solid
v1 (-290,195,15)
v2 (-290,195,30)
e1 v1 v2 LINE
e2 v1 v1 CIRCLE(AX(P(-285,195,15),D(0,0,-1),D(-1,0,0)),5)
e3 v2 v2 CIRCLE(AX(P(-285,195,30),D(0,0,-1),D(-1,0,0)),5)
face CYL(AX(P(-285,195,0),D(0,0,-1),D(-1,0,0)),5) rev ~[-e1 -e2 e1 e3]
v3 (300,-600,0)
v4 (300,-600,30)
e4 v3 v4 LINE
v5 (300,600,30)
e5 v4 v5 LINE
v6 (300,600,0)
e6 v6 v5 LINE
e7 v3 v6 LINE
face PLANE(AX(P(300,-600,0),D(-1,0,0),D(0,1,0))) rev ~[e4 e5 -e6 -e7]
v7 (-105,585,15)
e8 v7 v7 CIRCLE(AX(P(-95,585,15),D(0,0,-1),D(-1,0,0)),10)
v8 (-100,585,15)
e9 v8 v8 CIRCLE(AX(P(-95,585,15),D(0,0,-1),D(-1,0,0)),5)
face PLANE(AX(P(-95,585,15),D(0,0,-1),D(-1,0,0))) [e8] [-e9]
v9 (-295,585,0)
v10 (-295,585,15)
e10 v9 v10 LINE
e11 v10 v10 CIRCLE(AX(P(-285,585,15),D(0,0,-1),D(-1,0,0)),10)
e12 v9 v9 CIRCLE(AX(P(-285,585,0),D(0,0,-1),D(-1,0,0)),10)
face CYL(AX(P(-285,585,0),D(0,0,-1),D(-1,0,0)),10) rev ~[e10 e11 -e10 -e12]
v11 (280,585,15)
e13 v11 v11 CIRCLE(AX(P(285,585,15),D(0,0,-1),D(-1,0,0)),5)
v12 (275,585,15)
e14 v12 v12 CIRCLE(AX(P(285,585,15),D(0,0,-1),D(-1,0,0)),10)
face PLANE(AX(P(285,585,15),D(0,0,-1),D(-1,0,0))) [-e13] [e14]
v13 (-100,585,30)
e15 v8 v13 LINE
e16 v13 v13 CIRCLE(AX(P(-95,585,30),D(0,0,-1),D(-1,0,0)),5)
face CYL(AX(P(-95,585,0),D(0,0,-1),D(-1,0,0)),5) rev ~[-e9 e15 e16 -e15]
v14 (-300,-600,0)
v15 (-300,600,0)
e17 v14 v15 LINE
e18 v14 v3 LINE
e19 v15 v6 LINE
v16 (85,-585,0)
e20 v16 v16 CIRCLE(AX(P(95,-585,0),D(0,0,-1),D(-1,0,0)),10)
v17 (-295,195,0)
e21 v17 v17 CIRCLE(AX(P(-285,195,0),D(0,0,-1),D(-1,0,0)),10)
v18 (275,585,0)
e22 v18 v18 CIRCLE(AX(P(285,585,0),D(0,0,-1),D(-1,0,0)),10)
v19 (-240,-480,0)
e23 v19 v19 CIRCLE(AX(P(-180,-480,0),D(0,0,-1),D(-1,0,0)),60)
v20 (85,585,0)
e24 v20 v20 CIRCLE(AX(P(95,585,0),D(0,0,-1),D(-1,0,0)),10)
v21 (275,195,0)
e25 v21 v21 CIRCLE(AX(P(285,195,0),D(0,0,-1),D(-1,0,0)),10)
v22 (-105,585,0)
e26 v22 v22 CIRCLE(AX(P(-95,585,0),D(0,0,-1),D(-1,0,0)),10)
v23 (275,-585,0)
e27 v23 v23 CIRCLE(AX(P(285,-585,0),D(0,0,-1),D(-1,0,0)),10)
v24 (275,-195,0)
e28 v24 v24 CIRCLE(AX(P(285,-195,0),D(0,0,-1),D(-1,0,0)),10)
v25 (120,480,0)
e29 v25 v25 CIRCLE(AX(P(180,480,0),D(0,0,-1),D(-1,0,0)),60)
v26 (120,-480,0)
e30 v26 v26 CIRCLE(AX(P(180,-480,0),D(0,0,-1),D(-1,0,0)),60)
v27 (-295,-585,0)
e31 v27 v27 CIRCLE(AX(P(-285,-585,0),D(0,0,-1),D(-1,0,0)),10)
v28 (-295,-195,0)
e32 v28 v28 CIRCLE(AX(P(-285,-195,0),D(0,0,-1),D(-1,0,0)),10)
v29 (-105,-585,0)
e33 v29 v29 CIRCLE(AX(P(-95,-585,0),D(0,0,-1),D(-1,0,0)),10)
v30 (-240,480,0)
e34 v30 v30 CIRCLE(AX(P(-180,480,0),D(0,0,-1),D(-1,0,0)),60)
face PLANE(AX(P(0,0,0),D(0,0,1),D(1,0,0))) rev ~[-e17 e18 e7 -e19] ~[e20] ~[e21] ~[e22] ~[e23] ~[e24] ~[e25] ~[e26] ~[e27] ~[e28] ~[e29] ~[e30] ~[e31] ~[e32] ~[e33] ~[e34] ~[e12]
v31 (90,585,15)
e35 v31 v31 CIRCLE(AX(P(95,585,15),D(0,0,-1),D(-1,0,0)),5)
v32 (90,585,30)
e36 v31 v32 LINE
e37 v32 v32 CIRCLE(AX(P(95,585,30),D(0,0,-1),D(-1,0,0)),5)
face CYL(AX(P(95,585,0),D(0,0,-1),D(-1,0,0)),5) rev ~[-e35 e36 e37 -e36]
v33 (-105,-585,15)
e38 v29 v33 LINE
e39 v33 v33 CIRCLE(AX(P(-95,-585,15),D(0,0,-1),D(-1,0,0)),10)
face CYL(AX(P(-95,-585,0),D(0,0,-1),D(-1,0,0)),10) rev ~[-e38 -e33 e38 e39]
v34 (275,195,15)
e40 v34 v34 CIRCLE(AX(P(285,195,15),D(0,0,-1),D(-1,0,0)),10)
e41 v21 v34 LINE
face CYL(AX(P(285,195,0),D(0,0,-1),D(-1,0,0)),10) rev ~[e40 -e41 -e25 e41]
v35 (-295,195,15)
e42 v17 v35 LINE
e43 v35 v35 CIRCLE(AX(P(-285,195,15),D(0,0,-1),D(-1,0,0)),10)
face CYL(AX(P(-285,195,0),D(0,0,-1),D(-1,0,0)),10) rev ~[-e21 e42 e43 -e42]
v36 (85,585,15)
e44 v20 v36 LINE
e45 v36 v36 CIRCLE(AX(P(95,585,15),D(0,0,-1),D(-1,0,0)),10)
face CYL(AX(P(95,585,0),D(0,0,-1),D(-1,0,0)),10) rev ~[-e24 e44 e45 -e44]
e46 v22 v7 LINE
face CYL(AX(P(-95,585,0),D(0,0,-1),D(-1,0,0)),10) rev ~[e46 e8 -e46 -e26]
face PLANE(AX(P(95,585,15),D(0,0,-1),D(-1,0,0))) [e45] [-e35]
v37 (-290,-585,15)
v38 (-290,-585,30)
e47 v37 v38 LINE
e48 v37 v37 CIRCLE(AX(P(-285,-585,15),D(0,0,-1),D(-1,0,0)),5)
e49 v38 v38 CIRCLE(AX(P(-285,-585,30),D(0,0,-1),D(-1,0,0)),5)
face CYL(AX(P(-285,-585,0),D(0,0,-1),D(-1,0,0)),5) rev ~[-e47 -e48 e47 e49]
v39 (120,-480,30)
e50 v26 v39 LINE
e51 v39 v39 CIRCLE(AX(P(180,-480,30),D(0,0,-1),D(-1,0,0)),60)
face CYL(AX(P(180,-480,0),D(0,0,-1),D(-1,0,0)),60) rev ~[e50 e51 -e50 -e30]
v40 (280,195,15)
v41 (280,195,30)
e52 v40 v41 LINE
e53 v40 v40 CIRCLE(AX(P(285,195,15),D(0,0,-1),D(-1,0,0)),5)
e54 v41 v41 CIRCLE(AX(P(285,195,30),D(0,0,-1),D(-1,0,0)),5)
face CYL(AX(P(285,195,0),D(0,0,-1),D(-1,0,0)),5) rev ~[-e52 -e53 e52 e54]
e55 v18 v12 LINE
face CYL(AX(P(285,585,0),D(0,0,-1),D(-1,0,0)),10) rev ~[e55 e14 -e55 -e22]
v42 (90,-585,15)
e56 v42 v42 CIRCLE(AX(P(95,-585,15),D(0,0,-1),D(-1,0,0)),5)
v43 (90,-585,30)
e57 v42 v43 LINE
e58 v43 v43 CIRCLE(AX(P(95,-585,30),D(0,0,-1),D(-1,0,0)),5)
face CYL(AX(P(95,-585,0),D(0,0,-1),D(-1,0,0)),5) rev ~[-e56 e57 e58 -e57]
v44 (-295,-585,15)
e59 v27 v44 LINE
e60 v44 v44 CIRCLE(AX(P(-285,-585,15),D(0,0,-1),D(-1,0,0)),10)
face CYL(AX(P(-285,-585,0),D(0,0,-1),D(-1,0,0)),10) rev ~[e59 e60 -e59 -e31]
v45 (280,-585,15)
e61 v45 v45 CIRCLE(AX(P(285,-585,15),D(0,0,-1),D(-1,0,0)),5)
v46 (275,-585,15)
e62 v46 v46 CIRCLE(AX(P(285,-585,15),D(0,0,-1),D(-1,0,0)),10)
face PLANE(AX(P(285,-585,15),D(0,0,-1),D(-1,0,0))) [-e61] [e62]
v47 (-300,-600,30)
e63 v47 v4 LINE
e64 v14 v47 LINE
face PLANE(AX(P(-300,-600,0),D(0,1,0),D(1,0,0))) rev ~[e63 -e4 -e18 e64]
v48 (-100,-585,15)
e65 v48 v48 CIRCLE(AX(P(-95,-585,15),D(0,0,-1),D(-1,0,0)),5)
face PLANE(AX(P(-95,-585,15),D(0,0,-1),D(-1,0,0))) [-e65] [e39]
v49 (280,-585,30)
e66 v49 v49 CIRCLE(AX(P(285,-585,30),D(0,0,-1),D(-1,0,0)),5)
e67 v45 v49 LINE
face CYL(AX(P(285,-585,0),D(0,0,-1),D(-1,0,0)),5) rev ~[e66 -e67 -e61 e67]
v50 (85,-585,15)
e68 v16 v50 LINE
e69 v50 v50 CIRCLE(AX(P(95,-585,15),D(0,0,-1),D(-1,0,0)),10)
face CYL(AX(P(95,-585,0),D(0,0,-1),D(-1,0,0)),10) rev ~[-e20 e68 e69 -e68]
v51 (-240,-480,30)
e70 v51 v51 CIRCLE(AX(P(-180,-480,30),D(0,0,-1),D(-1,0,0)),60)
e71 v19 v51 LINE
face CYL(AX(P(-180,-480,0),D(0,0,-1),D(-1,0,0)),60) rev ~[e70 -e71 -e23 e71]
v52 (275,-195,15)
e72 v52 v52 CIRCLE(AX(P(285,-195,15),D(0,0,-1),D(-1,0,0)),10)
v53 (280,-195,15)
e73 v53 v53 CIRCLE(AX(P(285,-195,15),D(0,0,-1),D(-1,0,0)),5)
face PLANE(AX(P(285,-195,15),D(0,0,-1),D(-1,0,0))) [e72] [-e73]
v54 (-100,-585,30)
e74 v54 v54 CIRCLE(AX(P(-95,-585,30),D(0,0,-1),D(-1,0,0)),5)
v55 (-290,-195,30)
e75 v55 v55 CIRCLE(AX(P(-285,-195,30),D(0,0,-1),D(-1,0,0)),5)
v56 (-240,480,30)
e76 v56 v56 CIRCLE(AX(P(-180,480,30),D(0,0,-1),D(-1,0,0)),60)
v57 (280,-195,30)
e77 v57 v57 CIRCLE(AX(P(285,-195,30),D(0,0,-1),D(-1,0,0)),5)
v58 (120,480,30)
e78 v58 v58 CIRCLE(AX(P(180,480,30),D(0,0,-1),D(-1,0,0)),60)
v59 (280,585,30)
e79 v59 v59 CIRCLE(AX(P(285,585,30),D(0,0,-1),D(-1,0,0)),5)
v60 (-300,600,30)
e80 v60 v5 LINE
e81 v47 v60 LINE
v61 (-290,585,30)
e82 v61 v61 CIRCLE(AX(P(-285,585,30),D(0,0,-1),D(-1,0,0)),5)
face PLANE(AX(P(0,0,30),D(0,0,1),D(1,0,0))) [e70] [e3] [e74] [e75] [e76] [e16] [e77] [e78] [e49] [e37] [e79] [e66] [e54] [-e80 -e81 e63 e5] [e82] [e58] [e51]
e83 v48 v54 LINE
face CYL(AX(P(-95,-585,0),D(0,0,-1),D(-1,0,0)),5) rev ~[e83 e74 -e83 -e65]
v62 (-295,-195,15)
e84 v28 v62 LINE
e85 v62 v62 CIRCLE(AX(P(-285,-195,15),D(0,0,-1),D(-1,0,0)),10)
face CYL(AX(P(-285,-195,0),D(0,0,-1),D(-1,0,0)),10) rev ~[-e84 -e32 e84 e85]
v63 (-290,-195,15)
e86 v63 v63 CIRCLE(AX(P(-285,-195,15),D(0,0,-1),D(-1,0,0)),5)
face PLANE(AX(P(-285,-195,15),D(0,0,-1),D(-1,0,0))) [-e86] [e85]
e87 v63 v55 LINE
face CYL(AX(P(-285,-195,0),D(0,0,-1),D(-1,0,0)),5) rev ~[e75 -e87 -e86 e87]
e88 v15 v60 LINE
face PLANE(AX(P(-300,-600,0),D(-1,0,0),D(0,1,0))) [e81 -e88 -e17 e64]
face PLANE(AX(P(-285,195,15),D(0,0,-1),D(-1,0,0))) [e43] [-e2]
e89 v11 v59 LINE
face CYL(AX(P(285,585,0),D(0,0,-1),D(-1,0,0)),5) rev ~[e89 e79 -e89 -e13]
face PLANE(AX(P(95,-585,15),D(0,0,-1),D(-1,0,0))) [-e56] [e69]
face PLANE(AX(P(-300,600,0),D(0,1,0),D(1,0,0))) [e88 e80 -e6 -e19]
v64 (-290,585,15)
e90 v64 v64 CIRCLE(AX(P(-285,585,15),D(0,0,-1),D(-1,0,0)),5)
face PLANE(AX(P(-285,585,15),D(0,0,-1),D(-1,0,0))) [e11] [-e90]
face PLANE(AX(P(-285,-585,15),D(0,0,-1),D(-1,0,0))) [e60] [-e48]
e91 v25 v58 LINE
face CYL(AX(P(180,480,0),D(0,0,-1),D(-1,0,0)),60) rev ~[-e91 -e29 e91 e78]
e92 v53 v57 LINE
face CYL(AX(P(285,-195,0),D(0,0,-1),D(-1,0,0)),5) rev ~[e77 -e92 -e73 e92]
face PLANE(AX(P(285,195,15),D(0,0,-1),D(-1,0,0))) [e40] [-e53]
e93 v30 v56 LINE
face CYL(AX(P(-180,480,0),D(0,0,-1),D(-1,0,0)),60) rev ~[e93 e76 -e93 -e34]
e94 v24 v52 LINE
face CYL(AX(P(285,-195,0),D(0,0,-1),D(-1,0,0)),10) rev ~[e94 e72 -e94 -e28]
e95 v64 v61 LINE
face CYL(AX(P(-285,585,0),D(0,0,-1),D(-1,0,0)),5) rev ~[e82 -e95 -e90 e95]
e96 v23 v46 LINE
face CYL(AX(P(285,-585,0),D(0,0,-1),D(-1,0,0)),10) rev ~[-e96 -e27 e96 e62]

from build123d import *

# Parameters (mm, degrees)
SKETCH1_W                 = 600
SKETCH1_H                 = 1200
BOSS_EXTRUDE1_DEPTH       = 30
SKETCH2_R                 = 60
CUT_EXTRUDE1_DEPTH        = 42
SKETCH3_R                 = 5
CUT_EXTRUDE2_DEPTH        = 40
LPATTERN1_COUNT           = 4
LPATTERN1_PITCH           = 390
LPATTERN2_COUNT           = 2
LPATTERN2_PITCH           = 570
LPATTERN2_COPY_1_SKETCH_R = 5
LPATTERN2_COPY_1_DEPTH    = 40
LPATTERN2_COPY_2_SKETCH_R = 5
LPATTERN2_COPY_2_DEPTH    = 40
LPATTERN2_COPY_3_SKETCH_R = 5
LPATTERN2_COPY_3_DEPTH    = 40
LPATTERN3_COUNT           = 3
LPATTERN3_PITCH           = 190
LPATTERN4_COPY_1_SKETCH_R = 5
LPATTERN4_COPY_1_DEPTH    = 40
LPATTERN4_COPY_2_SKETCH_R = 5
LPATTERN4_COPY_2_DEPTH    = 40
LPATTERN4_COPY_3_SKETCH_R = 5
LPATTERN4_COPY_3_DEPTH    = 40
SKETCH4_R                 = 10
CUT_EXTRUDE3_DEPTH        = 15
LPATTERN5_COUNT           = 4
LPATTERN5_PITCH           = 390
LPATTERN6_COUNT           = 2
LPATTERN6_PITCH           = 570
LPATTERN6_COPY_1_SKETCH_R = 10
LPATTERN6_COPY_1_DEPTH    = 15
LPATTERN6_COPY_2_SKETCH_R = 10
LPATTERN6_COPY_2_DEPTH    = 15
LPATTERN6_COPY_3_SKETCH_R = 10
LPATTERN6_COPY_3_DEPTH    = 15
LPATTERN8_COUNT           = 3
LPATTERN8_PITCH           = 190
LPATTERN9_COPY_1_SKETCH_R = 10
LPATTERN9_COPY_1_DEPTH    = 15
LPATTERN9_COPY_2_SKETCH_R = 10
LPATTERN9_COPY_2_DEPTH    = 15
LPATTERN9_COPY_3_SKETCH_R = 10
LPATTERN9_COPY_3_DEPTH    = 15


with BuildPart() as part:
    # Sketch1 → Boss-Extrude1 (new body)
    with BuildSketch(Plane.XY):
        Rectangle(SKETCH1_W, SKETCH1_H)
    extrude(amount=BOSS_EXTRUDE1_DEPTH)

    # Sketch2 → Cut-Extrude1 (cut)
    with BuildSketch(Plane(origin=(0, 0, 0), x_dir=(-1, 0, 0), z_dir=(0, 0, -1))):
        with Locations((-180, 480)):
            Circle(SKETCH2_R)
        with Locations((180, 480)):
            Circle(SKETCH2_R)
        with Locations((180, -480)):
            Circle(SKETCH2_R)
        with Locations((-180, -480)):
            Circle(SKETCH2_R)
    extrude(amount=-CUT_EXTRUDE1_DEPTH, mode=Mode.SUBTRACT)

    # Sketch3 → Cut-Extrude2 (cut)
    with BuildSketch(Plane(origin=(0, 0, 0), x_dir=(-1, 0, 0), z_dir=(0, 0, -1))):
        with Locations((-285, 585)):
            Circle(SKETCH3_R)
    cut_extrude2 = extrude(amount=-CUT_EXTRUDE2_DEPTH, mode=Mode.SUBTRACT)

    # LPattern1: Cut-Extrude2 ×4
    with Locations(*[(0, -i * LPATTERN1_PITCH, 0) for i in range(1, LPATTERN1_COUNT)]):
        add(cut_extrude2, mode=Mode.SUBTRACT)

    # LPattern2: Cut-Extrude2 ×2
    with Locations(*[(-i * LPATTERN2_PITCH, 0, 0) for i in range(1, LPATTERN2_COUNT)]):
        add(cut_extrude2, mode=Mode.SUBTRACT)

    # LPattern2 copy 1 sketch → LPattern2 copy 1 (cut)
    with BuildSketch(Plane(origin=(-570, -390, 0), x_dir=(-1, 0, 0), z_dir=(0, 0, -1))):
        with Locations((-285, 585)):
            Circle(LPATTERN2_COPY_1_SKETCH_R)
    extrude(amount=-LPATTERN2_COPY_1_DEPTH, mode=Mode.SUBTRACT)

    # LPattern2 copy 2 sketch → LPattern2 copy 2 (cut)
    with BuildSketch(Plane(origin=(-570, -780, 0), x_dir=(-1, 0, 0), z_dir=(0, 0, -1))):
        with Locations((-285, 585)):
            Circle(LPATTERN2_COPY_2_SKETCH_R)
    extrude(amount=-LPATTERN2_COPY_2_DEPTH, mode=Mode.SUBTRACT)

    # LPattern2 copy 3 sketch → LPattern2 copy 3 (cut)
    with BuildSketch(Plane(origin=(-570, -1170, 0), x_dir=(-1, 0, 0), z_dir=(0, 0, -1))):
        with Locations((-285, 585)):
            Circle(LPATTERN2_COPY_3_SKETCH_R)
    extrude(amount=-LPATTERN2_COPY_3_DEPTH, mode=Mode.SUBTRACT)

    # LPattern3: Cut-Extrude2 ×3
    with Locations(*[(-i * LPATTERN3_PITCH, 0, 0) for i in range(1, LPATTERN3_COUNT)]):
        add(cut_extrude2, mode=Mode.SUBTRACT)

    # LPattern4 copy 1 sketch → LPattern4 copy 1 (cut)
    with BuildSketch(Plane(origin=(-190, -1170, 0), x_dir=(-1, 0, 0), z_dir=(0, 0, -1))):
        with Locations((-285, 585)):
            Circle(LPATTERN4_COPY_1_SKETCH_R)
    extrude(amount=-LPATTERN4_COPY_1_DEPTH, mode=Mode.SUBTRACT)

    # LPattern4 copy 2 sketch → LPattern4 copy 2 (cut)
    with BuildSketch(Plane(origin=(-380, -1170, 0), x_dir=(-1, 0, 0), z_dir=(0, 0, -1))):
        with Locations((-285, 585)):
            Circle(LPATTERN4_COPY_2_SKETCH_R)
    extrude(amount=-LPATTERN4_COPY_2_DEPTH, mode=Mode.SUBTRACT)

    # LPattern4 copy 3 sketch → LPattern4 copy 3 (cut)
    with BuildSketch(Plane(origin=(0, -1170, 0), x_dir=(-1, 0, 0), z_dir=(0, 0, -1))):
        with Locations((-285, 585)):
            Circle(LPATTERN4_COPY_3_SKETCH_R)
    extrude(amount=-LPATTERN4_COPY_3_DEPTH, mode=Mode.SUBTRACT)

    # Sketch4 → Cut-Extrude3 (cut)
    with BuildSketch(Plane(origin=(0, 0, 0), x_dir=(-1, 0, 0), z_dir=(0, 0, -1))):
        with Locations((-285, 585)):
            Circle(SKETCH4_R)
    cut_extrude3 = extrude(amount=-CUT_EXTRUDE3_DEPTH, mode=Mode.SUBTRACT)

    # LPattern5: Cut-Extrude3 ×4
    with Locations(*[(0, -i * LPATTERN5_PITCH, 0) for i in range(1, LPATTERN5_COUNT)]):
        add(cut_extrude3, mode=Mode.SUBTRACT)

    # LPattern6: Cut-Extrude3 ×2
    with Locations(*[(-i * LPATTERN6_PITCH, 0, 0) for i in range(1, LPATTERN6_COUNT)]):
        add(cut_extrude3, mode=Mode.SUBTRACT)

    # LPattern6 copy 1 sketch → LPattern6 copy 1 (cut)
    with BuildSketch(Plane(origin=(-570, -390, 0), x_dir=(-1, 0, 0), z_dir=(0, 0, -1))):
        with Locations((-285, 585)):
            Circle(LPATTERN6_COPY_1_SKETCH_R)
    extrude(amount=-LPATTERN6_COPY_1_DEPTH, mode=Mode.SUBTRACT)

    # LPattern6 copy 2 sketch → LPattern6 copy 2 (cut)
    with BuildSketch(Plane(origin=(-570, -780, 0), x_dir=(-1, 0, 0), z_dir=(0, 0, -1))):
        with Locations((-285, 585)):
            Circle(LPATTERN6_COPY_2_SKETCH_R)
    extrude(amount=-LPATTERN6_COPY_2_DEPTH, mode=Mode.SUBTRACT)

    # LPattern6 copy 3 sketch → LPattern6 copy 3 (cut)
    with BuildSketch(Plane(origin=(-570, -1170, 0), x_dir=(-1, 0, 0), z_dir=(0, 0, -1))):
        with Locations((-285, 585)):
            Circle(LPATTERN6_COPY_3_SKETCH_R)
    extrude(amount=-LPATTERN6_COPY_3_DEPTH, mode=Mode.SUBTRACT)

    # LPattern8: Cut-Extrude3 ×3
    with Locations(*[(-i * LPATTERN8_PITCH, 0, 0) for i in range(1, LPATTERN8_COUNT)]):
        add(cut_extrude3, mode=Mode.SUBTRACT)

    # LPattern9 copy 1 sketch → LPattern9 copy 1 (cut)
    with BuildSketch(Plane(origin=(-190, -1170, 0), x_dir=(-1, 0, 0), z_dir=(0, 0, -1))):
        with Locations((-285, 585)):
            Circle(LPATTERN9_COPY_1_SKETCH_R)
    extrude(amount=-LPATTERN9_COPY_1_DEPTH, mode=Mode.SUBTRACT)

    # LPattern9 copy 2 sketch → LPattern9 copy 2 (cut)
    with BuildSketch(Plane(origin=(-380, -1170, 0), x_dir=(-1, 0, 0), z_dir=(0, 0, -1))):
        with Locations((-285, 585)):
            Circle(LPATTERN9_COPY_2_SKETCH_R)
    extrude(amount=-LPATTERN9_COPY_2_DEPTH, mode=Mode.SUBTRACT)

    # LPattern9 copy 3 sketch → LPattern9 copy 3 (cut)
    with BuildSketch(Plane(origin=(0, -1170, 0), x_dir=(-1, 0, 0), z_dir=(0, 0, -1))):
        with Locations((-285, 585)):
            Circle(LPATTERN9_COPY_3_SKETCH_R)
    extrude(amount=-LPATTERN9_COPY_3_DEPTH, mode=Mode.SUBTRACT)


solid = part.part
